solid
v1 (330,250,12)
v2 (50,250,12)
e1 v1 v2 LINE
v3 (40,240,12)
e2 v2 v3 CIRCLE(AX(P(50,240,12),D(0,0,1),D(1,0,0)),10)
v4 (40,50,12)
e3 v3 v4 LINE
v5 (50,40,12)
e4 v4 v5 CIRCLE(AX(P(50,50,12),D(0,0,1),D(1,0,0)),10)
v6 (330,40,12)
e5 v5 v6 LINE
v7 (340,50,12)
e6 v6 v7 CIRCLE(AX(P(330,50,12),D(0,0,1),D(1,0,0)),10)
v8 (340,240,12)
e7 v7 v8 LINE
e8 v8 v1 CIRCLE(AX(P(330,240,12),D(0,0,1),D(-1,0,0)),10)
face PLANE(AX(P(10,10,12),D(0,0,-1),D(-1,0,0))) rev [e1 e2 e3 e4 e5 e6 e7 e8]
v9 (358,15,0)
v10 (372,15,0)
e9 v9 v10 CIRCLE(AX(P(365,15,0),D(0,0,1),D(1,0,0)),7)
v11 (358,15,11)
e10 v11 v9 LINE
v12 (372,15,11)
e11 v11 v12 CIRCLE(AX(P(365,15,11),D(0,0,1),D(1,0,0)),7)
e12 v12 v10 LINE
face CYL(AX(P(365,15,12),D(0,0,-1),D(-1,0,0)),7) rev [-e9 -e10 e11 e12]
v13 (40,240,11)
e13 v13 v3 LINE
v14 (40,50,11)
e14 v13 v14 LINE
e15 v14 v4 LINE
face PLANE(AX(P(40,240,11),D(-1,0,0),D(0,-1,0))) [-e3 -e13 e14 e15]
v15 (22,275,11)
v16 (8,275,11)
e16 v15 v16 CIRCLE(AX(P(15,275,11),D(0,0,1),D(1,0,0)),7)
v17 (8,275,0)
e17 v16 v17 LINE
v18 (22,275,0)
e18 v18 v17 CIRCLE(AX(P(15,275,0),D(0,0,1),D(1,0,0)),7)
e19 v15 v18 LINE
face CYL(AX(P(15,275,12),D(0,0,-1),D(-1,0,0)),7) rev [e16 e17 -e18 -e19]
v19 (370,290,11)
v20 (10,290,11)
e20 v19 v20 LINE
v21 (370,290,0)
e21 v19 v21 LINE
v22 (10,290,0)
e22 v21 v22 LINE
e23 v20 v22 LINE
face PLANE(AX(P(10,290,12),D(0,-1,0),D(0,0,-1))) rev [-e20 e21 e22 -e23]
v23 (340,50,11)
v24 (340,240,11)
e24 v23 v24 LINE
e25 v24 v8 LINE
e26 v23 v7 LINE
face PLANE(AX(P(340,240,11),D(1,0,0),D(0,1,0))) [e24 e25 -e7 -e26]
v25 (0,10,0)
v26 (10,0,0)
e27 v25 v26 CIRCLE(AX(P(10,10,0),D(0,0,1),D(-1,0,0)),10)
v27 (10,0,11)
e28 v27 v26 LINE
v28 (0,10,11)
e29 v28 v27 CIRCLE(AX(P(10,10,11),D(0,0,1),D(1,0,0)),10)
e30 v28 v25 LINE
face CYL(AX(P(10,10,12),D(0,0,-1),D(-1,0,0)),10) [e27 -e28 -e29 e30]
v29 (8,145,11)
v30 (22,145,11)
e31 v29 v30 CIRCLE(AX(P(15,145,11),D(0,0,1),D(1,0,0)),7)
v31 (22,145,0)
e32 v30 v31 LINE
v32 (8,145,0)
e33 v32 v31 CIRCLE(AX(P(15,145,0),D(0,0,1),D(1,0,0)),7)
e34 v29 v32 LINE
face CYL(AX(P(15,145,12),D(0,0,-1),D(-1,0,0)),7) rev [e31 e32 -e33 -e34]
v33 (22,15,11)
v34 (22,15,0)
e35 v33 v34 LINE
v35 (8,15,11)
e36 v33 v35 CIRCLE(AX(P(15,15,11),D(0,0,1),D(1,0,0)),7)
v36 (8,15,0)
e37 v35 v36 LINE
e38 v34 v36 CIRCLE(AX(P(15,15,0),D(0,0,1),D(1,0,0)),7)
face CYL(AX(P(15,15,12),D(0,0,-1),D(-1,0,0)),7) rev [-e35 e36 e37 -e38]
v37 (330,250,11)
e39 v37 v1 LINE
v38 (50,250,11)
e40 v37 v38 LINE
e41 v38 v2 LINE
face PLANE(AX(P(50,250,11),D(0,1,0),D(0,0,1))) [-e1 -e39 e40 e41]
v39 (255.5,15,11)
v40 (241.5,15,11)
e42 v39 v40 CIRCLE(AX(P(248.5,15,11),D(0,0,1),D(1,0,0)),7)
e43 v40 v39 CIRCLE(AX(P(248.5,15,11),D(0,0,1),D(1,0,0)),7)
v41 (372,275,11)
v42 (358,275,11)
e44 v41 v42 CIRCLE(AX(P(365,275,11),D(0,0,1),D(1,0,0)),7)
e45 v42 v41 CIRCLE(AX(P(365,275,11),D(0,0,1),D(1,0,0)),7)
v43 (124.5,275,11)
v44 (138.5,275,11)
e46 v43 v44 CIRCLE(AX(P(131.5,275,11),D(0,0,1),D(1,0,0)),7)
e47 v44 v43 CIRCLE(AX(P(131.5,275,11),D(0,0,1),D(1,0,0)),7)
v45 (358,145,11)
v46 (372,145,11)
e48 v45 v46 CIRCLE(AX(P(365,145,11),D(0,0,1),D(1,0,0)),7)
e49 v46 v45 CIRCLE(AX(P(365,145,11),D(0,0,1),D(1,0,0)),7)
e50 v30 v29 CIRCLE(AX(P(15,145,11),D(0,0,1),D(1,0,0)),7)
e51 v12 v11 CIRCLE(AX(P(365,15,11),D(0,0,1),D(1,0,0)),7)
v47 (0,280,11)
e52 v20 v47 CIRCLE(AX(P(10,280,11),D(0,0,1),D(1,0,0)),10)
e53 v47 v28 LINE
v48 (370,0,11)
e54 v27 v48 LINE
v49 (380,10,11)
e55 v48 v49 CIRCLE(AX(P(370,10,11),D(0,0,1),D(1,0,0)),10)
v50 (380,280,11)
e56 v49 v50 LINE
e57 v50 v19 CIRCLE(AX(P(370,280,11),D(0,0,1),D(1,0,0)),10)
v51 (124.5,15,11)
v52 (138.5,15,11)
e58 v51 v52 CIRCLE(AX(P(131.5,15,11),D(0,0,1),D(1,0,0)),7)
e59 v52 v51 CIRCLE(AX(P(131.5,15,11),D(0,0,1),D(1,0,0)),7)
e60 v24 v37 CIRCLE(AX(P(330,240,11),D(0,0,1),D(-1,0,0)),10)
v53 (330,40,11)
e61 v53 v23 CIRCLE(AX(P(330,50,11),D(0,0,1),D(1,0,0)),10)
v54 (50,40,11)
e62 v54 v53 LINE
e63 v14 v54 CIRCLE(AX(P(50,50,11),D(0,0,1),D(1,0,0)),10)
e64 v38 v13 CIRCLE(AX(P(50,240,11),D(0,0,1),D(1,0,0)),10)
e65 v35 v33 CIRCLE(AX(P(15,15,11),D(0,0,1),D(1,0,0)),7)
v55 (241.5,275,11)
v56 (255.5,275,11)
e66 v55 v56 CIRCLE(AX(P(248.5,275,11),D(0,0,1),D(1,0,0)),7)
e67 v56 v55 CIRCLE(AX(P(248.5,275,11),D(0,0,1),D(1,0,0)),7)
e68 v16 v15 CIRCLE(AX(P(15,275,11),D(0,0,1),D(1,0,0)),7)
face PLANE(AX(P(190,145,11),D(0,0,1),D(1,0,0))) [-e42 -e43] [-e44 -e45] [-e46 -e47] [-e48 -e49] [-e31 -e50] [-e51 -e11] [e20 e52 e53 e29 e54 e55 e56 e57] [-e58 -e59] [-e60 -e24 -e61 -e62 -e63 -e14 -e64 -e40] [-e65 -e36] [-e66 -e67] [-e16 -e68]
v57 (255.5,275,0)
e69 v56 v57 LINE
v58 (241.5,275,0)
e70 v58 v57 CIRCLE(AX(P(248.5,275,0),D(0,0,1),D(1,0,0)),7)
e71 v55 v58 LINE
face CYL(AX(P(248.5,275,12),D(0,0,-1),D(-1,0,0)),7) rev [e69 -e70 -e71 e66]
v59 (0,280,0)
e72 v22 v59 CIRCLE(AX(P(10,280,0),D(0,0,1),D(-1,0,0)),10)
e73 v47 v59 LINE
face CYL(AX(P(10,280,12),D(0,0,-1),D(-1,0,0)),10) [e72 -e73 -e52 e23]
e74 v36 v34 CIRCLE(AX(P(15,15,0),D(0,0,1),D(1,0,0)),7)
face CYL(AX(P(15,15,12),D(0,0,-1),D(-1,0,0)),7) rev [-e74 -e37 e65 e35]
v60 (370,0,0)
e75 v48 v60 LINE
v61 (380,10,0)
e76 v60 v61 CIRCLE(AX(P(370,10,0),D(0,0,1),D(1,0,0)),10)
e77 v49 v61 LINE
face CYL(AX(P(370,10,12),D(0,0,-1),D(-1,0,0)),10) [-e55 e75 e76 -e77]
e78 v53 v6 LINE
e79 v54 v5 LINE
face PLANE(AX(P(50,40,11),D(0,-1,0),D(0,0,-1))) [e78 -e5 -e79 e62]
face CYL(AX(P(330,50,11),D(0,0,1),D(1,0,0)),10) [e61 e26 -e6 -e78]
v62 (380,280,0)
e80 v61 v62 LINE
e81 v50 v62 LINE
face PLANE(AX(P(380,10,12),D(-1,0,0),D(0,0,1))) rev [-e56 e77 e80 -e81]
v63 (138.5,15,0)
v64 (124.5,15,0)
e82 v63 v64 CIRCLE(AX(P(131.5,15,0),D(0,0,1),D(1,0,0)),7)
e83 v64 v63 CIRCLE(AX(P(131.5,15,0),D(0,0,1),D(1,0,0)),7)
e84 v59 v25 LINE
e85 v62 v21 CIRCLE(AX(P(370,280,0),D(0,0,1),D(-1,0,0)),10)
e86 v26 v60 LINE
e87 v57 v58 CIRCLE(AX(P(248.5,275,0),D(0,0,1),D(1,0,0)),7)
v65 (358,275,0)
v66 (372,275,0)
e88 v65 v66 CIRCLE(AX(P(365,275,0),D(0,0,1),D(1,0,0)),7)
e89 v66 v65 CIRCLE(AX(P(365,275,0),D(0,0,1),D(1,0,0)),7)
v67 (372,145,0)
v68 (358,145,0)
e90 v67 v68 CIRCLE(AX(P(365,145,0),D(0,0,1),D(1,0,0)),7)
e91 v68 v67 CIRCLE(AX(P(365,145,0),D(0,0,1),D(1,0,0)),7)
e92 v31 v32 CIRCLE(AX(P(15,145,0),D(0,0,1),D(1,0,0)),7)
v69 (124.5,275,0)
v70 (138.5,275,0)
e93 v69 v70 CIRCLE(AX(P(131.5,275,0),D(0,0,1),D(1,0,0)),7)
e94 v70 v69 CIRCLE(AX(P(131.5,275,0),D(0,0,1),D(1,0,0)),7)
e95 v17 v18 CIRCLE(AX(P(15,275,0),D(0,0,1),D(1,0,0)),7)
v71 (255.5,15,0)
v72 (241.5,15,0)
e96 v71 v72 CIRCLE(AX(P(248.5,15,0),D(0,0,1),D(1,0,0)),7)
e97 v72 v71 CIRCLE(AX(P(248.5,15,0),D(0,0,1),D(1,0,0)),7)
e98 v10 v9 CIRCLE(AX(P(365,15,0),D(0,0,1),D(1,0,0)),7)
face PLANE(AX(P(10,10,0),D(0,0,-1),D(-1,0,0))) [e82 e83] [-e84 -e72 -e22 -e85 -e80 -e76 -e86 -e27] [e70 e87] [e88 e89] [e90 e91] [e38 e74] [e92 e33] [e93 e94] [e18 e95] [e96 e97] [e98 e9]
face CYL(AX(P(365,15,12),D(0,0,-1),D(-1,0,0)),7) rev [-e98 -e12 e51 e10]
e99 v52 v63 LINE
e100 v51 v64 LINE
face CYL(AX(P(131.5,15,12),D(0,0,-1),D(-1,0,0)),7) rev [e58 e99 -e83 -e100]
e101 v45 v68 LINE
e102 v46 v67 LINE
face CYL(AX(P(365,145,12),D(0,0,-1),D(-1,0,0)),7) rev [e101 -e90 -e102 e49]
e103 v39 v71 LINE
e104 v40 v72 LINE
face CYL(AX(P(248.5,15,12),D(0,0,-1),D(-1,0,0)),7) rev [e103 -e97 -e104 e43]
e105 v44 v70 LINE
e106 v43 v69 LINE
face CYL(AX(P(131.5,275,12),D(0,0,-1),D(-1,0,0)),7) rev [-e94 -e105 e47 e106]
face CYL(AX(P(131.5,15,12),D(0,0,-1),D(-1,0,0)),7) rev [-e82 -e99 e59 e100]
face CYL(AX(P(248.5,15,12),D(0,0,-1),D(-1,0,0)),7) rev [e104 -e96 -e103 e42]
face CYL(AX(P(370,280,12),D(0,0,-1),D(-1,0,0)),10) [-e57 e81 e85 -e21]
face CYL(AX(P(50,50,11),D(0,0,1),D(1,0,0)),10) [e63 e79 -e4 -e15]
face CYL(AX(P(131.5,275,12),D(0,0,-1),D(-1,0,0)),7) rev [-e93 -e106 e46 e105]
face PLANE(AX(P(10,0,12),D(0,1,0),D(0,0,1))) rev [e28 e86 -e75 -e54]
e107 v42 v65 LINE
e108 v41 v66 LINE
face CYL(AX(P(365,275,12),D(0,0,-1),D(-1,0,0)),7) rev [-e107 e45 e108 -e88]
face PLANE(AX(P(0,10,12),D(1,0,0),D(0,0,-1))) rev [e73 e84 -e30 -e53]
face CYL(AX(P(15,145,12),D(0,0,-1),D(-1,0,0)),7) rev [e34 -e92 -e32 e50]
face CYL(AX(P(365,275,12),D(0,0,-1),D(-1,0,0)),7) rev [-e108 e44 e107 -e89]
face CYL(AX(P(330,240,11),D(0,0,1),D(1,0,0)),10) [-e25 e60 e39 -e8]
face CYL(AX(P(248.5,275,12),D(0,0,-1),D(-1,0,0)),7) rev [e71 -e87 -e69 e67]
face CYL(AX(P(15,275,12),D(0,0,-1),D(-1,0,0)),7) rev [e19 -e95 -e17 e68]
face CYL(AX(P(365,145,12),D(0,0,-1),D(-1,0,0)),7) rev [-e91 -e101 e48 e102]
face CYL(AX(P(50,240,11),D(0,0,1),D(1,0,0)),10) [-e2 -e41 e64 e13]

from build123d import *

# Parameters (mm, degrees)
SKETCH1_R           = 7
BOSS_EXTRUDE1_DEPTH = 12
SKETCH2_OUTSIDE_W   = 477.634
SKETCH2_OUTSIDE_H   = 387.634
CUT_EXTRUDE1_DEPTH  = 1


with BuildPart() as part:
    # Sketch1 → Boss-Extrude1 (new body)
    with BuildSketch(Plane.XY):
        with BuildLine():
            Line((10, 0), (370, 0))
            ThreePointArc((370, 0), (377.071067812, 2.928932188), (380, 10))
            Line((380, 10), (380, 280))
            ThreePointArc((380, 280), (377.071067812, 287.071067812), (370, 290))
            Line((370, 290), (10, 290))
            ThreePointArc((10, 290), (2.928932188, 287.071067812), (0, 280))
            Line((0, 280), (0, 10))
            ThreePointArc((0, 10), (2.928932188, 2.928932188), (10, 0))
        make_face()
        with Locations((15, 275)):
            Circle(SKETCH1_R, mode=Mode.SUBTRACT)
        with Locations((131.5, 275)):
            Circle(SKETCH1_R, mode=Mode.SUBTRACT)
        with Locations((248.5, 275)):
            Circle(SKETCH1_R, mode=Mode.SUBTRACT)
        with Locations((365, 275)):
            Circle(SKETCH1_R, mode=Mode.SUBTRACT)
        with Locations((365, 145)):
            Circle(SKETCH1_R, mode=Mode.SUBTRACT)
        with Locations((365, 15)):
            Circle(SKETCH1_R, mode=Mode.SUBTRACT)
        with Locations((248.5, 15)):
            Circle(SKETCH1_R, mode=Mode.SUBTRACT)
        with Locations((131.5, 15)):
            Circle(SKETCH1_R, mode=Mode.SUBTRACT)
        with Locations((15, 15)):
            Circle(SKETCH1_R, mode=Mode.SUBTRACT)
        with Locations((15, 145)):
            Circle(SKETCH1_R, mode=Mode.SUBTRACT)
    extrude(amount=BOSS_EXTRUDE1_DEPTH)

    # Sketch2 outside → Cut-Extrude1 (cut)
    with BuildSketch(Plane.XY.offset(12)):
        with Locations((190, 145)):
            Rectangle(SKETCH2_OUTSIDE_W, SKETCH2_OUTSIDE_H)
        with BuildLine():
            Line((50, 250), (330, 250))
            ThreePointArc((330, 250), (337.071067812, 247.071067812), (340, 240))
            Line((340, 240), (340, 50))
            ThreePointArc((340, 50), (337.071067812, 42.928932188), (330, 40))
            Line((330, 40), (50, 40))
            ThreePointArc((50, 40), (42.928932188, 42.928932188), (40, 50))
            Line((40, 50), (40, 240))
            ThreePointArc((40, 240), (42.928932188, 247.071067812), (50, 250))
        make_face(mode=Mode.SUBTRACT)
    extrude(amount=-CUT_EXTRUDE1_DEPTH, mode=Mode.SUBTRACT)


solid = part.part
